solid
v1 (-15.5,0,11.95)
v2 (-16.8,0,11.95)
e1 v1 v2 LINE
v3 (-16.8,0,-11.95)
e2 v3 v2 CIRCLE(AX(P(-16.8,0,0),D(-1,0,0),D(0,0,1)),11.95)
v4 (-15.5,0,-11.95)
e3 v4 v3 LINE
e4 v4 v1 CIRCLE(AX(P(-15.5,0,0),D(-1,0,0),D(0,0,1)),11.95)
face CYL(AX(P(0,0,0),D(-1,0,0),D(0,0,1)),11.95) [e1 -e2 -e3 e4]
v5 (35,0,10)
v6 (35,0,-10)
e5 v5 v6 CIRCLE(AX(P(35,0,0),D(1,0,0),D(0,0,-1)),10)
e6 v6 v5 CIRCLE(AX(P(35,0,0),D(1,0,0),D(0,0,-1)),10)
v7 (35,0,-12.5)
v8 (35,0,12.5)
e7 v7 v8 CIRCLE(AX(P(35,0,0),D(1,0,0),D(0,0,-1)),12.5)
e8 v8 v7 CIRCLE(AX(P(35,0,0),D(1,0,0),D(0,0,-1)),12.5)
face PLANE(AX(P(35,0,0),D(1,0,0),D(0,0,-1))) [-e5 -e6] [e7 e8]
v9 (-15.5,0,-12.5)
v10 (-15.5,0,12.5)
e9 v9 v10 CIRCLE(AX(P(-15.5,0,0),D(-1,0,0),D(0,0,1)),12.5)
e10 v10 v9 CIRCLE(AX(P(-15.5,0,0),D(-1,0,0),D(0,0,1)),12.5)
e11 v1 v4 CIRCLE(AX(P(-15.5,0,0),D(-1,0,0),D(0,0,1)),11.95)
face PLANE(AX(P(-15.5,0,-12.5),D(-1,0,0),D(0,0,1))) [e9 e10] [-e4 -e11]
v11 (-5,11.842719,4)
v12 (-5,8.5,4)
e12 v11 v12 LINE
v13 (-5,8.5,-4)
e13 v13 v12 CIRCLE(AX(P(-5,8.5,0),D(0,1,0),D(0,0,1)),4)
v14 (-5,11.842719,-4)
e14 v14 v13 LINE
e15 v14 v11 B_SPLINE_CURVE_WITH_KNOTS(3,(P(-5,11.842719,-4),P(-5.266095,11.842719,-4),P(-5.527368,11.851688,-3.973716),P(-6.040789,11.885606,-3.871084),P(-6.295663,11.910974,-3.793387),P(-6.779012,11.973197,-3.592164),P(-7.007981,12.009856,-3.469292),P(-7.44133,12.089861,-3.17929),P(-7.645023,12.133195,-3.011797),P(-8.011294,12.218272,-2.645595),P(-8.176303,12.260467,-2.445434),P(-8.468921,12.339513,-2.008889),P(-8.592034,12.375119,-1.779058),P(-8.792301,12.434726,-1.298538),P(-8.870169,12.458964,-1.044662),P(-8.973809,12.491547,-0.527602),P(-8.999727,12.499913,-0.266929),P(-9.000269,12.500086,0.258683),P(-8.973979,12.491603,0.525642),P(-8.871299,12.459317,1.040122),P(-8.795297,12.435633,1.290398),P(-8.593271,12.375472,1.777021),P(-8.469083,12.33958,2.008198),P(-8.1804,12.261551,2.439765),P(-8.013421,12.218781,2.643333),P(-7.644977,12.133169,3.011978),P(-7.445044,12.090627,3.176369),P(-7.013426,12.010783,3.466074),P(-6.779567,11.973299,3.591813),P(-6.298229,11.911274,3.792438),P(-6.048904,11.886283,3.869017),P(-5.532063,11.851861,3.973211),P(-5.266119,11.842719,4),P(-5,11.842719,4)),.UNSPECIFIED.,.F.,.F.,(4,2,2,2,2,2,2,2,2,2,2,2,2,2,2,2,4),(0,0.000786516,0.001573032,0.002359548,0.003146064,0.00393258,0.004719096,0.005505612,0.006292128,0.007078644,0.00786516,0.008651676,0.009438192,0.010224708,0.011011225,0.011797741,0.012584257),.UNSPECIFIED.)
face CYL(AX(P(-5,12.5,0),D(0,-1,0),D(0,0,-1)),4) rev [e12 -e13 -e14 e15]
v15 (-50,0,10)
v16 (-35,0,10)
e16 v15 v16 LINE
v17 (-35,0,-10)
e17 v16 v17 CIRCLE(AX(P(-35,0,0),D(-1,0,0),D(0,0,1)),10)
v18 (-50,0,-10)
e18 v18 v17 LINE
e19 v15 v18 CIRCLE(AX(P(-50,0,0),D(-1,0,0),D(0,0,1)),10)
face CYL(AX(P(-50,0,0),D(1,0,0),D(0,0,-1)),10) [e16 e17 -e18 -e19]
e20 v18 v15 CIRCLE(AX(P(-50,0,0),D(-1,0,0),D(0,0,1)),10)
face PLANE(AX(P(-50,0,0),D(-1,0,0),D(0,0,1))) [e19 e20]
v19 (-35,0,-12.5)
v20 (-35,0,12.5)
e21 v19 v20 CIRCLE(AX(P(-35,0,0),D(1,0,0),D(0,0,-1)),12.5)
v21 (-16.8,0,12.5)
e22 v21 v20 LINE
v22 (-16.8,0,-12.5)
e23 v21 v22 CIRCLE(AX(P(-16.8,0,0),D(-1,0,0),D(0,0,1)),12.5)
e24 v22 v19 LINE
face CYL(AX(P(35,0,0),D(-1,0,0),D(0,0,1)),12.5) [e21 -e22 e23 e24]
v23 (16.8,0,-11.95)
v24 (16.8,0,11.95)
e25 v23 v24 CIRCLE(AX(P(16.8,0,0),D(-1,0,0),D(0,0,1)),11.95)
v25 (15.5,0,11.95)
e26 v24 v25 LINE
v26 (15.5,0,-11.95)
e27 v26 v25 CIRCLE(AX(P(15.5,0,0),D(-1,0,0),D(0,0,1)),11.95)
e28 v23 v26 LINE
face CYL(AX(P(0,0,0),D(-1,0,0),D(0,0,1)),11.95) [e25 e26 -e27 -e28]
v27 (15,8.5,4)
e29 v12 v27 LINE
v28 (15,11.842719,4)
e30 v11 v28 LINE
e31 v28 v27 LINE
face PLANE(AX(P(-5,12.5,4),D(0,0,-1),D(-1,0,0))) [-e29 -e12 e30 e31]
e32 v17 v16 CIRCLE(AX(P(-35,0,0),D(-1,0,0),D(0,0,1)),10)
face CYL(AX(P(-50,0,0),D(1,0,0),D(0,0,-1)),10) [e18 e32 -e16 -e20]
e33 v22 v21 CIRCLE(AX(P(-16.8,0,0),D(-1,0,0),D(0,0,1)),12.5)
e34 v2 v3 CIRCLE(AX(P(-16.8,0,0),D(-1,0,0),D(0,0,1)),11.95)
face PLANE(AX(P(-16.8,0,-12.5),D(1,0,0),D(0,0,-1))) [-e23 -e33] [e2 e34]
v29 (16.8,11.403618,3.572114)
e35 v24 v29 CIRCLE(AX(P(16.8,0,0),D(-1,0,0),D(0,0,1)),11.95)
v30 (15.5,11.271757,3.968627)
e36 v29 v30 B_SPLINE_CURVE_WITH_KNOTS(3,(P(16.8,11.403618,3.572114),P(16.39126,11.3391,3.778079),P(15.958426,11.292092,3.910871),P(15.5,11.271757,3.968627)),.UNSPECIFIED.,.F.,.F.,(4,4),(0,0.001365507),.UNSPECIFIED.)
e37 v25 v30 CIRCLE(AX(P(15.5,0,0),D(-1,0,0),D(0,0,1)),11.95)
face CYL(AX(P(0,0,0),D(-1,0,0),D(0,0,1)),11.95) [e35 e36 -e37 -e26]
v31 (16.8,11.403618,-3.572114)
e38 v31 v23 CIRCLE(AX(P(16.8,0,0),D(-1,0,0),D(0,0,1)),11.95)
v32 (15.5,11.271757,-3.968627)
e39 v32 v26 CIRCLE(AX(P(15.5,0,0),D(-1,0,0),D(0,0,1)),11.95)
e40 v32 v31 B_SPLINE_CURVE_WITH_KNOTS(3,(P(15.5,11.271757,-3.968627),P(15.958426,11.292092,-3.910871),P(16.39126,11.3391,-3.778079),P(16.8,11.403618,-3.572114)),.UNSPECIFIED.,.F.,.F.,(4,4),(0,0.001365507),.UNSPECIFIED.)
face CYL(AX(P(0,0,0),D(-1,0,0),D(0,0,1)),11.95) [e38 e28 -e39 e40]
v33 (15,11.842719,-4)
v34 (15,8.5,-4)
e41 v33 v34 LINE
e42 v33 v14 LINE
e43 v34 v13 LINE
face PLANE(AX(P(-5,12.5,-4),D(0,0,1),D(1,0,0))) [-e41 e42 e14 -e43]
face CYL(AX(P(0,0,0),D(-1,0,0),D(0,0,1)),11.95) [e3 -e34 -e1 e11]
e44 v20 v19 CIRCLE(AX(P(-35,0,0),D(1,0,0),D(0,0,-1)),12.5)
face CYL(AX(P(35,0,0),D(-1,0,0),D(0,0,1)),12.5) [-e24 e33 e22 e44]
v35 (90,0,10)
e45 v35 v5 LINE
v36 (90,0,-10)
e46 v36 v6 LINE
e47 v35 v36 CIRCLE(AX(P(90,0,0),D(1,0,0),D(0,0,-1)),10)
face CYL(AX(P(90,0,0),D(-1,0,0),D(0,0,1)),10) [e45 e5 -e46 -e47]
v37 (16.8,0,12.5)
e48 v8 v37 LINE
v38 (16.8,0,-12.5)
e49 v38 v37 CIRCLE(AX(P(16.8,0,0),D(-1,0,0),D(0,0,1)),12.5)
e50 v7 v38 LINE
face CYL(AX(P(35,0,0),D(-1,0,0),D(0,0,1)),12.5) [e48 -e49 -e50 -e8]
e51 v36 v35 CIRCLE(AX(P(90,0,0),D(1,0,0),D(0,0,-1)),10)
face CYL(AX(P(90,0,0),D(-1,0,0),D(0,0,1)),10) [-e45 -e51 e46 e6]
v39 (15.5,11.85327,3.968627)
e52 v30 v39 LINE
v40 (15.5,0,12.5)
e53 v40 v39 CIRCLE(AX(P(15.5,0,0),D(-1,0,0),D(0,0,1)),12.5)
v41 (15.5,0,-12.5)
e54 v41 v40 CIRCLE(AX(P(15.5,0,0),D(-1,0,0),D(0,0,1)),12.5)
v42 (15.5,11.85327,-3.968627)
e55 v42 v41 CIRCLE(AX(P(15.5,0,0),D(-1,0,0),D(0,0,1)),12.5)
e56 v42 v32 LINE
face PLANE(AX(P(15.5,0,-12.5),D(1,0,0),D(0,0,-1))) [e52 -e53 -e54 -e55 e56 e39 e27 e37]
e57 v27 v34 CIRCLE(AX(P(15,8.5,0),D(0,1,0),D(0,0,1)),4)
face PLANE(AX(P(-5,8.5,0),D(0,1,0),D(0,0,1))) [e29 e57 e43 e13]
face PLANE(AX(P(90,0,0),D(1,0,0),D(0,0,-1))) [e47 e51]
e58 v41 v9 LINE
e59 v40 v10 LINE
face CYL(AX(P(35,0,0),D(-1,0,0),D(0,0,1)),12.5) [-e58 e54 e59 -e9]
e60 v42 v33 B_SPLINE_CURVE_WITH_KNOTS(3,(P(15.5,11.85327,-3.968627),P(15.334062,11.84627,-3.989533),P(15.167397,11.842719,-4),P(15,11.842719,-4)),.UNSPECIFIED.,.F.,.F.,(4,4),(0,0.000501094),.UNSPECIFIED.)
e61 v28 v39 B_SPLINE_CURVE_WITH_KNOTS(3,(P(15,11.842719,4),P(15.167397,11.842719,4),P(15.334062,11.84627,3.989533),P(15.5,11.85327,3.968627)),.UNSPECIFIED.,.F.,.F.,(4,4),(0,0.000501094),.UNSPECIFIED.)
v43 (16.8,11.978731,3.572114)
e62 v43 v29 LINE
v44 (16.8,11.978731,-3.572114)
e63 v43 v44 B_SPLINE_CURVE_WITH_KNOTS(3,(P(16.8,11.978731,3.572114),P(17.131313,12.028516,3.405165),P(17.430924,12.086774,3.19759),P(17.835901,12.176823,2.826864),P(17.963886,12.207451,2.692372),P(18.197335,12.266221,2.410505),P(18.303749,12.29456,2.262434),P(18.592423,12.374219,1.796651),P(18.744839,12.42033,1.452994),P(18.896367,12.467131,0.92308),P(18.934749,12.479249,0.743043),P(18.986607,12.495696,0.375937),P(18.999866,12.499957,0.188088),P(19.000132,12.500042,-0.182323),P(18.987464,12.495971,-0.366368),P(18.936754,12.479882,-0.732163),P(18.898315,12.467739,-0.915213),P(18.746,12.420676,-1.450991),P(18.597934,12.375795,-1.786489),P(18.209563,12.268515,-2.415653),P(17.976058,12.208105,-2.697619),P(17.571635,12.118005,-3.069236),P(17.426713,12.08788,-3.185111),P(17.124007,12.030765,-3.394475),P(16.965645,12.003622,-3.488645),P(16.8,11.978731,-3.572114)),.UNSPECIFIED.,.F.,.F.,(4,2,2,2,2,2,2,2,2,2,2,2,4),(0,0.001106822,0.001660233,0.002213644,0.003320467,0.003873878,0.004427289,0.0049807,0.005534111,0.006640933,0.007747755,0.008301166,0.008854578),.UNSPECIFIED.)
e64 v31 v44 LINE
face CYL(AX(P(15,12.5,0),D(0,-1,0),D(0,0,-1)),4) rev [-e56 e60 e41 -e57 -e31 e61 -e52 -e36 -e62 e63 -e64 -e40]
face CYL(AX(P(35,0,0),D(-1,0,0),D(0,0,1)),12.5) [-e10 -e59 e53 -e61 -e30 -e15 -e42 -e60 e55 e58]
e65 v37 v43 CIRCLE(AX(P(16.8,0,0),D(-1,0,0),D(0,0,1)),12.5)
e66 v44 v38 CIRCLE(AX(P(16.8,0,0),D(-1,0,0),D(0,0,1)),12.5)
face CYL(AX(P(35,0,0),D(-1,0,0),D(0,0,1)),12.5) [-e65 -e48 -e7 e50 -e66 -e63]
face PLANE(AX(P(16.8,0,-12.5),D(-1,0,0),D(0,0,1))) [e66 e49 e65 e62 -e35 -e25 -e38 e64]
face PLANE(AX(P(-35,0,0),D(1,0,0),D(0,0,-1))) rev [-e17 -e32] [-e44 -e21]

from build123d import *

# Parameters (mm, degrees)
SKETCH_1_R          = 12.5
EXTRUDE_1_DEPTH     = 35
SKETCH_3_R          = 10
EXTRUDE_3_DEPTH     = 55
SKETCH_4_W          = 1.3
SKETCH_4_H          = 0.55
CUT_EXTRUDE_1_DEPTH = 94.259047818
EXTRUDE_START       = 15
SKETCH_6_R          = 10
EXTRUDE_4_DEPTH     = 15


with BuildPart() as part:
    # 草图1 → 凸台-拉伸1 (new, symmetric)
    with BuildSketch(Plane(origin=(0, 0, 0), x_dir=(0, 0, -1), z_dir=(1, 0, 0))):
        Circle(SKETCH_1_R)
    extrude(amount=EXTRUDE_1_DEPTH, both=True)

    # 草图3 → 凸台-拉伸3 (add)
    with BuildSketch(Plane(origin=(35, 0, 0), x_dir=(0, 0, -1), z_dir=(1, 0, 0))):
        Circle(SKETCH_3_R)
    extrude(amount=EXTRUDE_3_DEPTH)

    # 草图4 → 切除-旋转1 (revolve, cut)
    with BuildSketch(Plane(origin=(0, 0, 0), x_dir=(1, 0, 0), z_dir=(0, 1, 0)), mode=Mode.PRIVATE) as cut_revolve_1_sk:
        with Locations((-16.15, 12.225)):
            Rectangle(SKETCH_4_W, SKETCH_4_H)
        with Locations((16.15, 12.225)):
            Rectangle(SKETCH_4_W, SKETCH_4_H)
    revolve(cut_revolve_1_sk.sketch.rotate(Axis((0, 0, 0), (1, 0, 0)), 180), axis=Axis((0, 0, 0), (1, 0, 0)), mode=Mode.SUBTRACT)

    # 草图5 → 切除-拉伸1 (cut, through all)
    with BuildSketch(Plane(origin=(0, 8.5, 0), x_dir=(1, 0, 0), z_dir=(0, 1, 0))):
        with BuildLine():
            Line((-5, 4), (15, 4))
            ThreePointArc((15, 4), (19, 0), (15, -4))
            Line((15, -4), (-5, -4))
            ThreePointArc((-5, -4), (-9, 0), (-5, 4))
        make_face()
    extrude(amount=CUT_EXTRUDE_1_DEPTH, mode=Mode.SUBTRACT)

    # 草图6 → 凸台-拉伸4 (add)
    with BuildSketch(Plane.ZY.offset(35).offset(EXTRUDE_START)):
        with Locations(Location((0, 0, 0), (0, 0, 180))):
            Circle(SKETCH_6_R)
    extrude(amount=-EXTRUDE_4_DEPTH)


solid = part.part
